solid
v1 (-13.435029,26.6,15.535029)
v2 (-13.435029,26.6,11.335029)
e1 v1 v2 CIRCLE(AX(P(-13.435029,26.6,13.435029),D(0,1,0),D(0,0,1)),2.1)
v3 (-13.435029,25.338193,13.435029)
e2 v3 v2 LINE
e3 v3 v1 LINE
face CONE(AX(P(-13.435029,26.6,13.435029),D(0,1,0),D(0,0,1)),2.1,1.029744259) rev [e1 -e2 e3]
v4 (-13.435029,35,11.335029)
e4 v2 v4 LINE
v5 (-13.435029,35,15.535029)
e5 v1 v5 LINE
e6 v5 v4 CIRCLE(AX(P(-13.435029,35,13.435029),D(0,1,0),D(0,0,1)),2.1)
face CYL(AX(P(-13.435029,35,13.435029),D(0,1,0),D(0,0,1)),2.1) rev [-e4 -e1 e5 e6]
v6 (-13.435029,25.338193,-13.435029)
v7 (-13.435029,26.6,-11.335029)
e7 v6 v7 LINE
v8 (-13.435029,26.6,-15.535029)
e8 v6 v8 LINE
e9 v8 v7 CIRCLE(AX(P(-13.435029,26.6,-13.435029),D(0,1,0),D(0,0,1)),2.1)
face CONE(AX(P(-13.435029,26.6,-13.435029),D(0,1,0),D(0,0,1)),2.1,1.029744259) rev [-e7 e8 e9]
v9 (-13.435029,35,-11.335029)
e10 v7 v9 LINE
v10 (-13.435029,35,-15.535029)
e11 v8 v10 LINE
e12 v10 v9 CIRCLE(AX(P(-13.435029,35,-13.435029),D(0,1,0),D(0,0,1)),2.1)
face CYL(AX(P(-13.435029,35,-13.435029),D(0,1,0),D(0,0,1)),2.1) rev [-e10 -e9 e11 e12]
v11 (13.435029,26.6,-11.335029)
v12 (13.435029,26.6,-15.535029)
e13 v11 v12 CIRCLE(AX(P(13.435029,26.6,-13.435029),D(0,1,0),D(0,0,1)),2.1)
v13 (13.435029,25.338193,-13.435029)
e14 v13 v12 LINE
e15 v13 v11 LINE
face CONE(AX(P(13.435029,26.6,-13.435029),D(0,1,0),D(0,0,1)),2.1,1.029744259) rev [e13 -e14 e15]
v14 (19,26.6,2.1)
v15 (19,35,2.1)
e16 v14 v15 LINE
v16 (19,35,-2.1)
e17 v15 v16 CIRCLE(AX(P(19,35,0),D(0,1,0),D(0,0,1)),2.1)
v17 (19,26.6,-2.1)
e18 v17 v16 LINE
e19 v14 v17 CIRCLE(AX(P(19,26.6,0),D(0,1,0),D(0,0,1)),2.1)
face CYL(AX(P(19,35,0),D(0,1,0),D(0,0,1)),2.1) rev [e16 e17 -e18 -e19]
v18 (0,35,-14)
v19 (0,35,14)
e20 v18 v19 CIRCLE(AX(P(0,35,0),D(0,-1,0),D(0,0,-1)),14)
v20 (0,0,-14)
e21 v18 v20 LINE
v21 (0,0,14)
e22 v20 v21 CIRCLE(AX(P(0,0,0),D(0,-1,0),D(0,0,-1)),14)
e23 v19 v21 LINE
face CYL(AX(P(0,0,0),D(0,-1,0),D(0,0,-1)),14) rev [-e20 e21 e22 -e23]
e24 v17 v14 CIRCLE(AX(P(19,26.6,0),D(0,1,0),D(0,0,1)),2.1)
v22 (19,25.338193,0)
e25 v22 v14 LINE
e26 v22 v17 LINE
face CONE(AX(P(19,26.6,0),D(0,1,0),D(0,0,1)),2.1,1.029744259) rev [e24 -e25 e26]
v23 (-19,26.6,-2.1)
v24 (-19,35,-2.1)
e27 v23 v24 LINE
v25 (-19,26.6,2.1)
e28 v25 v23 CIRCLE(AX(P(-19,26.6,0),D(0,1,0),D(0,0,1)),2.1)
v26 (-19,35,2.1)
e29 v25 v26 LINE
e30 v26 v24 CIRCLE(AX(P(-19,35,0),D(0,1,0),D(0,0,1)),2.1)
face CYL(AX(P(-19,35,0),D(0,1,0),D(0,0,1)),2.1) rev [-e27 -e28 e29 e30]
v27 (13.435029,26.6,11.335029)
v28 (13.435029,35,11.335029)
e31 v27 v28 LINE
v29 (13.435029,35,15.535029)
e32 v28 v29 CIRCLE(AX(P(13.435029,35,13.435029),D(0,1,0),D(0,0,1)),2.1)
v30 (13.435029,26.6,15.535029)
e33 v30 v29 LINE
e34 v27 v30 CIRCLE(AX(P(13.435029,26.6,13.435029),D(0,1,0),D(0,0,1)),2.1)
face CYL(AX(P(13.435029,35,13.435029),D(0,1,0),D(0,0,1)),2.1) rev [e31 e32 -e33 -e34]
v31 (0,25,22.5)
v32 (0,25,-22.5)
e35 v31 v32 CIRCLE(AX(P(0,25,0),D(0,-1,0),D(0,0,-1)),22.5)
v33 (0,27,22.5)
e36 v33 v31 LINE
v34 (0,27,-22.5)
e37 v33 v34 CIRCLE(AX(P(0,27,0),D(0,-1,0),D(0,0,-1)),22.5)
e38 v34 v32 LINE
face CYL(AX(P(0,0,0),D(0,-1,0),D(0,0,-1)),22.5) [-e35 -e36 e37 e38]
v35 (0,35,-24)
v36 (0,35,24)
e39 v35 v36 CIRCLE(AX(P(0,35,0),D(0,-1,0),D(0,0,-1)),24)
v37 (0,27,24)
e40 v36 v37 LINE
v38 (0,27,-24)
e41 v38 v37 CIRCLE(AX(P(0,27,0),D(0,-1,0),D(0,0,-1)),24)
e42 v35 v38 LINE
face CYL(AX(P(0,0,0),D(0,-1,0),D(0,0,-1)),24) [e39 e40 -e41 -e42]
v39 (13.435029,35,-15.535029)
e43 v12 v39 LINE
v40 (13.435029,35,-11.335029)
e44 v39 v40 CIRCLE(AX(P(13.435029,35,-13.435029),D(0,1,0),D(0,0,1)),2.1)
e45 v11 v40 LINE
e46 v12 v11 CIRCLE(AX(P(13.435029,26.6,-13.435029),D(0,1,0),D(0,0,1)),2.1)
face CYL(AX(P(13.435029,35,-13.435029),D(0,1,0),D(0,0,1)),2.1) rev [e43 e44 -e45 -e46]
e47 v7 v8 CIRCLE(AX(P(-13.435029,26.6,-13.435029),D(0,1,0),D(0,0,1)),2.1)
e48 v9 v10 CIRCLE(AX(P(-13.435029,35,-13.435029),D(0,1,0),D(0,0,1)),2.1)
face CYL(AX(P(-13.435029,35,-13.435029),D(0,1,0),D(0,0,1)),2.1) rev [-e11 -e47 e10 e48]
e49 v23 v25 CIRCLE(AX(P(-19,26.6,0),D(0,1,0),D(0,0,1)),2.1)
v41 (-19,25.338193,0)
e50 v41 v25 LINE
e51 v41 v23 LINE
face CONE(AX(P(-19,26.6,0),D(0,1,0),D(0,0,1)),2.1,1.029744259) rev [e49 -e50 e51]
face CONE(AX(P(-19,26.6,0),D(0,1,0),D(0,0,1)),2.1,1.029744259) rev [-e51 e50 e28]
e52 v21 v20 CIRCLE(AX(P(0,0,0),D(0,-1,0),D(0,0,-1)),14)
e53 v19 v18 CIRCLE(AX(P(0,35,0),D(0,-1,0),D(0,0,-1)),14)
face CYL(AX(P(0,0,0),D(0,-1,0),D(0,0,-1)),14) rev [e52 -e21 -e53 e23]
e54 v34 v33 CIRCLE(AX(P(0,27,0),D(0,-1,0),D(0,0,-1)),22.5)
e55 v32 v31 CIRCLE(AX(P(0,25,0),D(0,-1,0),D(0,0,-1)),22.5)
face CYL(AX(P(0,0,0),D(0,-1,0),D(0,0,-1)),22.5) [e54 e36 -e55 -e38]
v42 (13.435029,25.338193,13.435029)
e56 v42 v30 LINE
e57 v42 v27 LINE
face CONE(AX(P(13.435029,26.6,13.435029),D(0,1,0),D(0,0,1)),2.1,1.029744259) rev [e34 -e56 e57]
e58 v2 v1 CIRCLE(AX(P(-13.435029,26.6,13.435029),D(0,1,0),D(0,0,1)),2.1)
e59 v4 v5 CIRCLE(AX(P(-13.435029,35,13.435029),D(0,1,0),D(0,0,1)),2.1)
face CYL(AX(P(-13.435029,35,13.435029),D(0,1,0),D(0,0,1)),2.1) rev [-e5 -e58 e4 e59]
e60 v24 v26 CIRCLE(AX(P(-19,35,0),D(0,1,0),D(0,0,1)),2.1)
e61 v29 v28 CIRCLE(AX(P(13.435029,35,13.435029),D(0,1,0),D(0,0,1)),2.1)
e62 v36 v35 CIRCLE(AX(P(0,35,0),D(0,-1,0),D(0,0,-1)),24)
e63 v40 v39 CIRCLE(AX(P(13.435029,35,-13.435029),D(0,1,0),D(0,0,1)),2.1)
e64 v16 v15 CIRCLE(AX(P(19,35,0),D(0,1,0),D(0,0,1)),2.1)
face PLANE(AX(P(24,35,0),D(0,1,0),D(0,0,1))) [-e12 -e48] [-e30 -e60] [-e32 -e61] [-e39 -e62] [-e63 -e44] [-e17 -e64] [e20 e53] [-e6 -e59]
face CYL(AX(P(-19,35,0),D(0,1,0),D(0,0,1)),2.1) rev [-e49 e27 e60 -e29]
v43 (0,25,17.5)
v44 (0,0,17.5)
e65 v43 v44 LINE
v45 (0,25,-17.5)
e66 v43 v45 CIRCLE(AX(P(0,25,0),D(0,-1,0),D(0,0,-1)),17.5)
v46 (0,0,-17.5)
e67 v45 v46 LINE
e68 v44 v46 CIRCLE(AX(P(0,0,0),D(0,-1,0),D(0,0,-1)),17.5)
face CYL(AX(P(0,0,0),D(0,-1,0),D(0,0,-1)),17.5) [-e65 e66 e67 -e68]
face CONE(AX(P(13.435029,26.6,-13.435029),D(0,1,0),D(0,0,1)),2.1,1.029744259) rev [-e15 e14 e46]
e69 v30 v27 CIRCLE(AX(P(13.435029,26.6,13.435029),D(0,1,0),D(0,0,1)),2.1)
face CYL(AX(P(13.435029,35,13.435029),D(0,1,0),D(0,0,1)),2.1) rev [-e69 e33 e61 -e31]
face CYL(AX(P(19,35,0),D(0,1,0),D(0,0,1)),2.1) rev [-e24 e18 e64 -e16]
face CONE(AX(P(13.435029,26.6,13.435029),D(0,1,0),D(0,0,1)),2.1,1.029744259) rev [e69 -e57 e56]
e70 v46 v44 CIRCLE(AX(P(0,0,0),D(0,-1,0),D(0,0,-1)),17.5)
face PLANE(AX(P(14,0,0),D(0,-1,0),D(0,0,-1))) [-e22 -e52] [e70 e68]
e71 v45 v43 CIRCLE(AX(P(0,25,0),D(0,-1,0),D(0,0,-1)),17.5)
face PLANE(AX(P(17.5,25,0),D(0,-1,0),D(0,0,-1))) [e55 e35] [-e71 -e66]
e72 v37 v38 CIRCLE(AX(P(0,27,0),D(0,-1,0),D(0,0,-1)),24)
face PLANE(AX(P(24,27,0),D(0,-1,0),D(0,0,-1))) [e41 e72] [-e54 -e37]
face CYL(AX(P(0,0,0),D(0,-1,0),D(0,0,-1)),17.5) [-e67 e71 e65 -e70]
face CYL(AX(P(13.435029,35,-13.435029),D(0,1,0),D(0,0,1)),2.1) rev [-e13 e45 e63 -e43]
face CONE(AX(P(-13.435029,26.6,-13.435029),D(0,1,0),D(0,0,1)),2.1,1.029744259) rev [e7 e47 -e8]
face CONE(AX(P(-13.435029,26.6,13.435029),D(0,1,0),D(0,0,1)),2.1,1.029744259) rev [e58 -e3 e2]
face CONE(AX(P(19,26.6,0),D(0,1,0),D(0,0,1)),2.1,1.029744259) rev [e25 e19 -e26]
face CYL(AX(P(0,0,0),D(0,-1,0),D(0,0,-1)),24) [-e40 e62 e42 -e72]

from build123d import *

# Parameters (mm, degrees)
M5_TAPPED_HOLE1_D     = 4.2
M5_TAPPED_HOLE1_DEPTH = 8.4
M5_TAPPED_HOLE1_TIP   = 1.2618073


with BuildPart() as part:
    # Sketch1 → Revolve1 (revolve)
    with BuildSketch(Plane.XY, mode=Mode.PRIVATE) as revolve1_sk:
        Polygon((14, 0), (17.5, 0), (17.5, 25), (22.5, 25), (22.5, 27), (24, 27), (24, 35), (14, 35), align=None)
    revolve(revolve1_sk.sketch.rotate(Axis((0, 0, 0), (0, 1, 0)), 90), axis=Axis((0, 0, 0), (0, 1, 0)))

    # M5 Tapped Hole1
    with Locations(Plane(origin=(0, 35, 0), x_dir=(1, 0, 0), z_dir=(0, 1, 0))):
        with Locations((-19, 0), (19, 0), (13.435028843, 13.435028843), (13.435028843, -13.435028843), (-13.435028843, -13.435028843), (-13.435028843, 13.435028843)):
            Hole(M5_TAPPED_HOLE1_D / 2, depth=M5_TAPPED_HOLE1_DEPTH)
            with Locations((0, 0, -(M5_TAPPED_HOLE1_DEPTH + M5_TAPPED_HOLE1_TIP / 2))):  # 118° drill point
                Cone(0, M5_TAPPED_HOLE1_D / 2, M5_TAPPED_HOLE1_TIP, mode=Mode.SUBTRACT)


solid = part.part
